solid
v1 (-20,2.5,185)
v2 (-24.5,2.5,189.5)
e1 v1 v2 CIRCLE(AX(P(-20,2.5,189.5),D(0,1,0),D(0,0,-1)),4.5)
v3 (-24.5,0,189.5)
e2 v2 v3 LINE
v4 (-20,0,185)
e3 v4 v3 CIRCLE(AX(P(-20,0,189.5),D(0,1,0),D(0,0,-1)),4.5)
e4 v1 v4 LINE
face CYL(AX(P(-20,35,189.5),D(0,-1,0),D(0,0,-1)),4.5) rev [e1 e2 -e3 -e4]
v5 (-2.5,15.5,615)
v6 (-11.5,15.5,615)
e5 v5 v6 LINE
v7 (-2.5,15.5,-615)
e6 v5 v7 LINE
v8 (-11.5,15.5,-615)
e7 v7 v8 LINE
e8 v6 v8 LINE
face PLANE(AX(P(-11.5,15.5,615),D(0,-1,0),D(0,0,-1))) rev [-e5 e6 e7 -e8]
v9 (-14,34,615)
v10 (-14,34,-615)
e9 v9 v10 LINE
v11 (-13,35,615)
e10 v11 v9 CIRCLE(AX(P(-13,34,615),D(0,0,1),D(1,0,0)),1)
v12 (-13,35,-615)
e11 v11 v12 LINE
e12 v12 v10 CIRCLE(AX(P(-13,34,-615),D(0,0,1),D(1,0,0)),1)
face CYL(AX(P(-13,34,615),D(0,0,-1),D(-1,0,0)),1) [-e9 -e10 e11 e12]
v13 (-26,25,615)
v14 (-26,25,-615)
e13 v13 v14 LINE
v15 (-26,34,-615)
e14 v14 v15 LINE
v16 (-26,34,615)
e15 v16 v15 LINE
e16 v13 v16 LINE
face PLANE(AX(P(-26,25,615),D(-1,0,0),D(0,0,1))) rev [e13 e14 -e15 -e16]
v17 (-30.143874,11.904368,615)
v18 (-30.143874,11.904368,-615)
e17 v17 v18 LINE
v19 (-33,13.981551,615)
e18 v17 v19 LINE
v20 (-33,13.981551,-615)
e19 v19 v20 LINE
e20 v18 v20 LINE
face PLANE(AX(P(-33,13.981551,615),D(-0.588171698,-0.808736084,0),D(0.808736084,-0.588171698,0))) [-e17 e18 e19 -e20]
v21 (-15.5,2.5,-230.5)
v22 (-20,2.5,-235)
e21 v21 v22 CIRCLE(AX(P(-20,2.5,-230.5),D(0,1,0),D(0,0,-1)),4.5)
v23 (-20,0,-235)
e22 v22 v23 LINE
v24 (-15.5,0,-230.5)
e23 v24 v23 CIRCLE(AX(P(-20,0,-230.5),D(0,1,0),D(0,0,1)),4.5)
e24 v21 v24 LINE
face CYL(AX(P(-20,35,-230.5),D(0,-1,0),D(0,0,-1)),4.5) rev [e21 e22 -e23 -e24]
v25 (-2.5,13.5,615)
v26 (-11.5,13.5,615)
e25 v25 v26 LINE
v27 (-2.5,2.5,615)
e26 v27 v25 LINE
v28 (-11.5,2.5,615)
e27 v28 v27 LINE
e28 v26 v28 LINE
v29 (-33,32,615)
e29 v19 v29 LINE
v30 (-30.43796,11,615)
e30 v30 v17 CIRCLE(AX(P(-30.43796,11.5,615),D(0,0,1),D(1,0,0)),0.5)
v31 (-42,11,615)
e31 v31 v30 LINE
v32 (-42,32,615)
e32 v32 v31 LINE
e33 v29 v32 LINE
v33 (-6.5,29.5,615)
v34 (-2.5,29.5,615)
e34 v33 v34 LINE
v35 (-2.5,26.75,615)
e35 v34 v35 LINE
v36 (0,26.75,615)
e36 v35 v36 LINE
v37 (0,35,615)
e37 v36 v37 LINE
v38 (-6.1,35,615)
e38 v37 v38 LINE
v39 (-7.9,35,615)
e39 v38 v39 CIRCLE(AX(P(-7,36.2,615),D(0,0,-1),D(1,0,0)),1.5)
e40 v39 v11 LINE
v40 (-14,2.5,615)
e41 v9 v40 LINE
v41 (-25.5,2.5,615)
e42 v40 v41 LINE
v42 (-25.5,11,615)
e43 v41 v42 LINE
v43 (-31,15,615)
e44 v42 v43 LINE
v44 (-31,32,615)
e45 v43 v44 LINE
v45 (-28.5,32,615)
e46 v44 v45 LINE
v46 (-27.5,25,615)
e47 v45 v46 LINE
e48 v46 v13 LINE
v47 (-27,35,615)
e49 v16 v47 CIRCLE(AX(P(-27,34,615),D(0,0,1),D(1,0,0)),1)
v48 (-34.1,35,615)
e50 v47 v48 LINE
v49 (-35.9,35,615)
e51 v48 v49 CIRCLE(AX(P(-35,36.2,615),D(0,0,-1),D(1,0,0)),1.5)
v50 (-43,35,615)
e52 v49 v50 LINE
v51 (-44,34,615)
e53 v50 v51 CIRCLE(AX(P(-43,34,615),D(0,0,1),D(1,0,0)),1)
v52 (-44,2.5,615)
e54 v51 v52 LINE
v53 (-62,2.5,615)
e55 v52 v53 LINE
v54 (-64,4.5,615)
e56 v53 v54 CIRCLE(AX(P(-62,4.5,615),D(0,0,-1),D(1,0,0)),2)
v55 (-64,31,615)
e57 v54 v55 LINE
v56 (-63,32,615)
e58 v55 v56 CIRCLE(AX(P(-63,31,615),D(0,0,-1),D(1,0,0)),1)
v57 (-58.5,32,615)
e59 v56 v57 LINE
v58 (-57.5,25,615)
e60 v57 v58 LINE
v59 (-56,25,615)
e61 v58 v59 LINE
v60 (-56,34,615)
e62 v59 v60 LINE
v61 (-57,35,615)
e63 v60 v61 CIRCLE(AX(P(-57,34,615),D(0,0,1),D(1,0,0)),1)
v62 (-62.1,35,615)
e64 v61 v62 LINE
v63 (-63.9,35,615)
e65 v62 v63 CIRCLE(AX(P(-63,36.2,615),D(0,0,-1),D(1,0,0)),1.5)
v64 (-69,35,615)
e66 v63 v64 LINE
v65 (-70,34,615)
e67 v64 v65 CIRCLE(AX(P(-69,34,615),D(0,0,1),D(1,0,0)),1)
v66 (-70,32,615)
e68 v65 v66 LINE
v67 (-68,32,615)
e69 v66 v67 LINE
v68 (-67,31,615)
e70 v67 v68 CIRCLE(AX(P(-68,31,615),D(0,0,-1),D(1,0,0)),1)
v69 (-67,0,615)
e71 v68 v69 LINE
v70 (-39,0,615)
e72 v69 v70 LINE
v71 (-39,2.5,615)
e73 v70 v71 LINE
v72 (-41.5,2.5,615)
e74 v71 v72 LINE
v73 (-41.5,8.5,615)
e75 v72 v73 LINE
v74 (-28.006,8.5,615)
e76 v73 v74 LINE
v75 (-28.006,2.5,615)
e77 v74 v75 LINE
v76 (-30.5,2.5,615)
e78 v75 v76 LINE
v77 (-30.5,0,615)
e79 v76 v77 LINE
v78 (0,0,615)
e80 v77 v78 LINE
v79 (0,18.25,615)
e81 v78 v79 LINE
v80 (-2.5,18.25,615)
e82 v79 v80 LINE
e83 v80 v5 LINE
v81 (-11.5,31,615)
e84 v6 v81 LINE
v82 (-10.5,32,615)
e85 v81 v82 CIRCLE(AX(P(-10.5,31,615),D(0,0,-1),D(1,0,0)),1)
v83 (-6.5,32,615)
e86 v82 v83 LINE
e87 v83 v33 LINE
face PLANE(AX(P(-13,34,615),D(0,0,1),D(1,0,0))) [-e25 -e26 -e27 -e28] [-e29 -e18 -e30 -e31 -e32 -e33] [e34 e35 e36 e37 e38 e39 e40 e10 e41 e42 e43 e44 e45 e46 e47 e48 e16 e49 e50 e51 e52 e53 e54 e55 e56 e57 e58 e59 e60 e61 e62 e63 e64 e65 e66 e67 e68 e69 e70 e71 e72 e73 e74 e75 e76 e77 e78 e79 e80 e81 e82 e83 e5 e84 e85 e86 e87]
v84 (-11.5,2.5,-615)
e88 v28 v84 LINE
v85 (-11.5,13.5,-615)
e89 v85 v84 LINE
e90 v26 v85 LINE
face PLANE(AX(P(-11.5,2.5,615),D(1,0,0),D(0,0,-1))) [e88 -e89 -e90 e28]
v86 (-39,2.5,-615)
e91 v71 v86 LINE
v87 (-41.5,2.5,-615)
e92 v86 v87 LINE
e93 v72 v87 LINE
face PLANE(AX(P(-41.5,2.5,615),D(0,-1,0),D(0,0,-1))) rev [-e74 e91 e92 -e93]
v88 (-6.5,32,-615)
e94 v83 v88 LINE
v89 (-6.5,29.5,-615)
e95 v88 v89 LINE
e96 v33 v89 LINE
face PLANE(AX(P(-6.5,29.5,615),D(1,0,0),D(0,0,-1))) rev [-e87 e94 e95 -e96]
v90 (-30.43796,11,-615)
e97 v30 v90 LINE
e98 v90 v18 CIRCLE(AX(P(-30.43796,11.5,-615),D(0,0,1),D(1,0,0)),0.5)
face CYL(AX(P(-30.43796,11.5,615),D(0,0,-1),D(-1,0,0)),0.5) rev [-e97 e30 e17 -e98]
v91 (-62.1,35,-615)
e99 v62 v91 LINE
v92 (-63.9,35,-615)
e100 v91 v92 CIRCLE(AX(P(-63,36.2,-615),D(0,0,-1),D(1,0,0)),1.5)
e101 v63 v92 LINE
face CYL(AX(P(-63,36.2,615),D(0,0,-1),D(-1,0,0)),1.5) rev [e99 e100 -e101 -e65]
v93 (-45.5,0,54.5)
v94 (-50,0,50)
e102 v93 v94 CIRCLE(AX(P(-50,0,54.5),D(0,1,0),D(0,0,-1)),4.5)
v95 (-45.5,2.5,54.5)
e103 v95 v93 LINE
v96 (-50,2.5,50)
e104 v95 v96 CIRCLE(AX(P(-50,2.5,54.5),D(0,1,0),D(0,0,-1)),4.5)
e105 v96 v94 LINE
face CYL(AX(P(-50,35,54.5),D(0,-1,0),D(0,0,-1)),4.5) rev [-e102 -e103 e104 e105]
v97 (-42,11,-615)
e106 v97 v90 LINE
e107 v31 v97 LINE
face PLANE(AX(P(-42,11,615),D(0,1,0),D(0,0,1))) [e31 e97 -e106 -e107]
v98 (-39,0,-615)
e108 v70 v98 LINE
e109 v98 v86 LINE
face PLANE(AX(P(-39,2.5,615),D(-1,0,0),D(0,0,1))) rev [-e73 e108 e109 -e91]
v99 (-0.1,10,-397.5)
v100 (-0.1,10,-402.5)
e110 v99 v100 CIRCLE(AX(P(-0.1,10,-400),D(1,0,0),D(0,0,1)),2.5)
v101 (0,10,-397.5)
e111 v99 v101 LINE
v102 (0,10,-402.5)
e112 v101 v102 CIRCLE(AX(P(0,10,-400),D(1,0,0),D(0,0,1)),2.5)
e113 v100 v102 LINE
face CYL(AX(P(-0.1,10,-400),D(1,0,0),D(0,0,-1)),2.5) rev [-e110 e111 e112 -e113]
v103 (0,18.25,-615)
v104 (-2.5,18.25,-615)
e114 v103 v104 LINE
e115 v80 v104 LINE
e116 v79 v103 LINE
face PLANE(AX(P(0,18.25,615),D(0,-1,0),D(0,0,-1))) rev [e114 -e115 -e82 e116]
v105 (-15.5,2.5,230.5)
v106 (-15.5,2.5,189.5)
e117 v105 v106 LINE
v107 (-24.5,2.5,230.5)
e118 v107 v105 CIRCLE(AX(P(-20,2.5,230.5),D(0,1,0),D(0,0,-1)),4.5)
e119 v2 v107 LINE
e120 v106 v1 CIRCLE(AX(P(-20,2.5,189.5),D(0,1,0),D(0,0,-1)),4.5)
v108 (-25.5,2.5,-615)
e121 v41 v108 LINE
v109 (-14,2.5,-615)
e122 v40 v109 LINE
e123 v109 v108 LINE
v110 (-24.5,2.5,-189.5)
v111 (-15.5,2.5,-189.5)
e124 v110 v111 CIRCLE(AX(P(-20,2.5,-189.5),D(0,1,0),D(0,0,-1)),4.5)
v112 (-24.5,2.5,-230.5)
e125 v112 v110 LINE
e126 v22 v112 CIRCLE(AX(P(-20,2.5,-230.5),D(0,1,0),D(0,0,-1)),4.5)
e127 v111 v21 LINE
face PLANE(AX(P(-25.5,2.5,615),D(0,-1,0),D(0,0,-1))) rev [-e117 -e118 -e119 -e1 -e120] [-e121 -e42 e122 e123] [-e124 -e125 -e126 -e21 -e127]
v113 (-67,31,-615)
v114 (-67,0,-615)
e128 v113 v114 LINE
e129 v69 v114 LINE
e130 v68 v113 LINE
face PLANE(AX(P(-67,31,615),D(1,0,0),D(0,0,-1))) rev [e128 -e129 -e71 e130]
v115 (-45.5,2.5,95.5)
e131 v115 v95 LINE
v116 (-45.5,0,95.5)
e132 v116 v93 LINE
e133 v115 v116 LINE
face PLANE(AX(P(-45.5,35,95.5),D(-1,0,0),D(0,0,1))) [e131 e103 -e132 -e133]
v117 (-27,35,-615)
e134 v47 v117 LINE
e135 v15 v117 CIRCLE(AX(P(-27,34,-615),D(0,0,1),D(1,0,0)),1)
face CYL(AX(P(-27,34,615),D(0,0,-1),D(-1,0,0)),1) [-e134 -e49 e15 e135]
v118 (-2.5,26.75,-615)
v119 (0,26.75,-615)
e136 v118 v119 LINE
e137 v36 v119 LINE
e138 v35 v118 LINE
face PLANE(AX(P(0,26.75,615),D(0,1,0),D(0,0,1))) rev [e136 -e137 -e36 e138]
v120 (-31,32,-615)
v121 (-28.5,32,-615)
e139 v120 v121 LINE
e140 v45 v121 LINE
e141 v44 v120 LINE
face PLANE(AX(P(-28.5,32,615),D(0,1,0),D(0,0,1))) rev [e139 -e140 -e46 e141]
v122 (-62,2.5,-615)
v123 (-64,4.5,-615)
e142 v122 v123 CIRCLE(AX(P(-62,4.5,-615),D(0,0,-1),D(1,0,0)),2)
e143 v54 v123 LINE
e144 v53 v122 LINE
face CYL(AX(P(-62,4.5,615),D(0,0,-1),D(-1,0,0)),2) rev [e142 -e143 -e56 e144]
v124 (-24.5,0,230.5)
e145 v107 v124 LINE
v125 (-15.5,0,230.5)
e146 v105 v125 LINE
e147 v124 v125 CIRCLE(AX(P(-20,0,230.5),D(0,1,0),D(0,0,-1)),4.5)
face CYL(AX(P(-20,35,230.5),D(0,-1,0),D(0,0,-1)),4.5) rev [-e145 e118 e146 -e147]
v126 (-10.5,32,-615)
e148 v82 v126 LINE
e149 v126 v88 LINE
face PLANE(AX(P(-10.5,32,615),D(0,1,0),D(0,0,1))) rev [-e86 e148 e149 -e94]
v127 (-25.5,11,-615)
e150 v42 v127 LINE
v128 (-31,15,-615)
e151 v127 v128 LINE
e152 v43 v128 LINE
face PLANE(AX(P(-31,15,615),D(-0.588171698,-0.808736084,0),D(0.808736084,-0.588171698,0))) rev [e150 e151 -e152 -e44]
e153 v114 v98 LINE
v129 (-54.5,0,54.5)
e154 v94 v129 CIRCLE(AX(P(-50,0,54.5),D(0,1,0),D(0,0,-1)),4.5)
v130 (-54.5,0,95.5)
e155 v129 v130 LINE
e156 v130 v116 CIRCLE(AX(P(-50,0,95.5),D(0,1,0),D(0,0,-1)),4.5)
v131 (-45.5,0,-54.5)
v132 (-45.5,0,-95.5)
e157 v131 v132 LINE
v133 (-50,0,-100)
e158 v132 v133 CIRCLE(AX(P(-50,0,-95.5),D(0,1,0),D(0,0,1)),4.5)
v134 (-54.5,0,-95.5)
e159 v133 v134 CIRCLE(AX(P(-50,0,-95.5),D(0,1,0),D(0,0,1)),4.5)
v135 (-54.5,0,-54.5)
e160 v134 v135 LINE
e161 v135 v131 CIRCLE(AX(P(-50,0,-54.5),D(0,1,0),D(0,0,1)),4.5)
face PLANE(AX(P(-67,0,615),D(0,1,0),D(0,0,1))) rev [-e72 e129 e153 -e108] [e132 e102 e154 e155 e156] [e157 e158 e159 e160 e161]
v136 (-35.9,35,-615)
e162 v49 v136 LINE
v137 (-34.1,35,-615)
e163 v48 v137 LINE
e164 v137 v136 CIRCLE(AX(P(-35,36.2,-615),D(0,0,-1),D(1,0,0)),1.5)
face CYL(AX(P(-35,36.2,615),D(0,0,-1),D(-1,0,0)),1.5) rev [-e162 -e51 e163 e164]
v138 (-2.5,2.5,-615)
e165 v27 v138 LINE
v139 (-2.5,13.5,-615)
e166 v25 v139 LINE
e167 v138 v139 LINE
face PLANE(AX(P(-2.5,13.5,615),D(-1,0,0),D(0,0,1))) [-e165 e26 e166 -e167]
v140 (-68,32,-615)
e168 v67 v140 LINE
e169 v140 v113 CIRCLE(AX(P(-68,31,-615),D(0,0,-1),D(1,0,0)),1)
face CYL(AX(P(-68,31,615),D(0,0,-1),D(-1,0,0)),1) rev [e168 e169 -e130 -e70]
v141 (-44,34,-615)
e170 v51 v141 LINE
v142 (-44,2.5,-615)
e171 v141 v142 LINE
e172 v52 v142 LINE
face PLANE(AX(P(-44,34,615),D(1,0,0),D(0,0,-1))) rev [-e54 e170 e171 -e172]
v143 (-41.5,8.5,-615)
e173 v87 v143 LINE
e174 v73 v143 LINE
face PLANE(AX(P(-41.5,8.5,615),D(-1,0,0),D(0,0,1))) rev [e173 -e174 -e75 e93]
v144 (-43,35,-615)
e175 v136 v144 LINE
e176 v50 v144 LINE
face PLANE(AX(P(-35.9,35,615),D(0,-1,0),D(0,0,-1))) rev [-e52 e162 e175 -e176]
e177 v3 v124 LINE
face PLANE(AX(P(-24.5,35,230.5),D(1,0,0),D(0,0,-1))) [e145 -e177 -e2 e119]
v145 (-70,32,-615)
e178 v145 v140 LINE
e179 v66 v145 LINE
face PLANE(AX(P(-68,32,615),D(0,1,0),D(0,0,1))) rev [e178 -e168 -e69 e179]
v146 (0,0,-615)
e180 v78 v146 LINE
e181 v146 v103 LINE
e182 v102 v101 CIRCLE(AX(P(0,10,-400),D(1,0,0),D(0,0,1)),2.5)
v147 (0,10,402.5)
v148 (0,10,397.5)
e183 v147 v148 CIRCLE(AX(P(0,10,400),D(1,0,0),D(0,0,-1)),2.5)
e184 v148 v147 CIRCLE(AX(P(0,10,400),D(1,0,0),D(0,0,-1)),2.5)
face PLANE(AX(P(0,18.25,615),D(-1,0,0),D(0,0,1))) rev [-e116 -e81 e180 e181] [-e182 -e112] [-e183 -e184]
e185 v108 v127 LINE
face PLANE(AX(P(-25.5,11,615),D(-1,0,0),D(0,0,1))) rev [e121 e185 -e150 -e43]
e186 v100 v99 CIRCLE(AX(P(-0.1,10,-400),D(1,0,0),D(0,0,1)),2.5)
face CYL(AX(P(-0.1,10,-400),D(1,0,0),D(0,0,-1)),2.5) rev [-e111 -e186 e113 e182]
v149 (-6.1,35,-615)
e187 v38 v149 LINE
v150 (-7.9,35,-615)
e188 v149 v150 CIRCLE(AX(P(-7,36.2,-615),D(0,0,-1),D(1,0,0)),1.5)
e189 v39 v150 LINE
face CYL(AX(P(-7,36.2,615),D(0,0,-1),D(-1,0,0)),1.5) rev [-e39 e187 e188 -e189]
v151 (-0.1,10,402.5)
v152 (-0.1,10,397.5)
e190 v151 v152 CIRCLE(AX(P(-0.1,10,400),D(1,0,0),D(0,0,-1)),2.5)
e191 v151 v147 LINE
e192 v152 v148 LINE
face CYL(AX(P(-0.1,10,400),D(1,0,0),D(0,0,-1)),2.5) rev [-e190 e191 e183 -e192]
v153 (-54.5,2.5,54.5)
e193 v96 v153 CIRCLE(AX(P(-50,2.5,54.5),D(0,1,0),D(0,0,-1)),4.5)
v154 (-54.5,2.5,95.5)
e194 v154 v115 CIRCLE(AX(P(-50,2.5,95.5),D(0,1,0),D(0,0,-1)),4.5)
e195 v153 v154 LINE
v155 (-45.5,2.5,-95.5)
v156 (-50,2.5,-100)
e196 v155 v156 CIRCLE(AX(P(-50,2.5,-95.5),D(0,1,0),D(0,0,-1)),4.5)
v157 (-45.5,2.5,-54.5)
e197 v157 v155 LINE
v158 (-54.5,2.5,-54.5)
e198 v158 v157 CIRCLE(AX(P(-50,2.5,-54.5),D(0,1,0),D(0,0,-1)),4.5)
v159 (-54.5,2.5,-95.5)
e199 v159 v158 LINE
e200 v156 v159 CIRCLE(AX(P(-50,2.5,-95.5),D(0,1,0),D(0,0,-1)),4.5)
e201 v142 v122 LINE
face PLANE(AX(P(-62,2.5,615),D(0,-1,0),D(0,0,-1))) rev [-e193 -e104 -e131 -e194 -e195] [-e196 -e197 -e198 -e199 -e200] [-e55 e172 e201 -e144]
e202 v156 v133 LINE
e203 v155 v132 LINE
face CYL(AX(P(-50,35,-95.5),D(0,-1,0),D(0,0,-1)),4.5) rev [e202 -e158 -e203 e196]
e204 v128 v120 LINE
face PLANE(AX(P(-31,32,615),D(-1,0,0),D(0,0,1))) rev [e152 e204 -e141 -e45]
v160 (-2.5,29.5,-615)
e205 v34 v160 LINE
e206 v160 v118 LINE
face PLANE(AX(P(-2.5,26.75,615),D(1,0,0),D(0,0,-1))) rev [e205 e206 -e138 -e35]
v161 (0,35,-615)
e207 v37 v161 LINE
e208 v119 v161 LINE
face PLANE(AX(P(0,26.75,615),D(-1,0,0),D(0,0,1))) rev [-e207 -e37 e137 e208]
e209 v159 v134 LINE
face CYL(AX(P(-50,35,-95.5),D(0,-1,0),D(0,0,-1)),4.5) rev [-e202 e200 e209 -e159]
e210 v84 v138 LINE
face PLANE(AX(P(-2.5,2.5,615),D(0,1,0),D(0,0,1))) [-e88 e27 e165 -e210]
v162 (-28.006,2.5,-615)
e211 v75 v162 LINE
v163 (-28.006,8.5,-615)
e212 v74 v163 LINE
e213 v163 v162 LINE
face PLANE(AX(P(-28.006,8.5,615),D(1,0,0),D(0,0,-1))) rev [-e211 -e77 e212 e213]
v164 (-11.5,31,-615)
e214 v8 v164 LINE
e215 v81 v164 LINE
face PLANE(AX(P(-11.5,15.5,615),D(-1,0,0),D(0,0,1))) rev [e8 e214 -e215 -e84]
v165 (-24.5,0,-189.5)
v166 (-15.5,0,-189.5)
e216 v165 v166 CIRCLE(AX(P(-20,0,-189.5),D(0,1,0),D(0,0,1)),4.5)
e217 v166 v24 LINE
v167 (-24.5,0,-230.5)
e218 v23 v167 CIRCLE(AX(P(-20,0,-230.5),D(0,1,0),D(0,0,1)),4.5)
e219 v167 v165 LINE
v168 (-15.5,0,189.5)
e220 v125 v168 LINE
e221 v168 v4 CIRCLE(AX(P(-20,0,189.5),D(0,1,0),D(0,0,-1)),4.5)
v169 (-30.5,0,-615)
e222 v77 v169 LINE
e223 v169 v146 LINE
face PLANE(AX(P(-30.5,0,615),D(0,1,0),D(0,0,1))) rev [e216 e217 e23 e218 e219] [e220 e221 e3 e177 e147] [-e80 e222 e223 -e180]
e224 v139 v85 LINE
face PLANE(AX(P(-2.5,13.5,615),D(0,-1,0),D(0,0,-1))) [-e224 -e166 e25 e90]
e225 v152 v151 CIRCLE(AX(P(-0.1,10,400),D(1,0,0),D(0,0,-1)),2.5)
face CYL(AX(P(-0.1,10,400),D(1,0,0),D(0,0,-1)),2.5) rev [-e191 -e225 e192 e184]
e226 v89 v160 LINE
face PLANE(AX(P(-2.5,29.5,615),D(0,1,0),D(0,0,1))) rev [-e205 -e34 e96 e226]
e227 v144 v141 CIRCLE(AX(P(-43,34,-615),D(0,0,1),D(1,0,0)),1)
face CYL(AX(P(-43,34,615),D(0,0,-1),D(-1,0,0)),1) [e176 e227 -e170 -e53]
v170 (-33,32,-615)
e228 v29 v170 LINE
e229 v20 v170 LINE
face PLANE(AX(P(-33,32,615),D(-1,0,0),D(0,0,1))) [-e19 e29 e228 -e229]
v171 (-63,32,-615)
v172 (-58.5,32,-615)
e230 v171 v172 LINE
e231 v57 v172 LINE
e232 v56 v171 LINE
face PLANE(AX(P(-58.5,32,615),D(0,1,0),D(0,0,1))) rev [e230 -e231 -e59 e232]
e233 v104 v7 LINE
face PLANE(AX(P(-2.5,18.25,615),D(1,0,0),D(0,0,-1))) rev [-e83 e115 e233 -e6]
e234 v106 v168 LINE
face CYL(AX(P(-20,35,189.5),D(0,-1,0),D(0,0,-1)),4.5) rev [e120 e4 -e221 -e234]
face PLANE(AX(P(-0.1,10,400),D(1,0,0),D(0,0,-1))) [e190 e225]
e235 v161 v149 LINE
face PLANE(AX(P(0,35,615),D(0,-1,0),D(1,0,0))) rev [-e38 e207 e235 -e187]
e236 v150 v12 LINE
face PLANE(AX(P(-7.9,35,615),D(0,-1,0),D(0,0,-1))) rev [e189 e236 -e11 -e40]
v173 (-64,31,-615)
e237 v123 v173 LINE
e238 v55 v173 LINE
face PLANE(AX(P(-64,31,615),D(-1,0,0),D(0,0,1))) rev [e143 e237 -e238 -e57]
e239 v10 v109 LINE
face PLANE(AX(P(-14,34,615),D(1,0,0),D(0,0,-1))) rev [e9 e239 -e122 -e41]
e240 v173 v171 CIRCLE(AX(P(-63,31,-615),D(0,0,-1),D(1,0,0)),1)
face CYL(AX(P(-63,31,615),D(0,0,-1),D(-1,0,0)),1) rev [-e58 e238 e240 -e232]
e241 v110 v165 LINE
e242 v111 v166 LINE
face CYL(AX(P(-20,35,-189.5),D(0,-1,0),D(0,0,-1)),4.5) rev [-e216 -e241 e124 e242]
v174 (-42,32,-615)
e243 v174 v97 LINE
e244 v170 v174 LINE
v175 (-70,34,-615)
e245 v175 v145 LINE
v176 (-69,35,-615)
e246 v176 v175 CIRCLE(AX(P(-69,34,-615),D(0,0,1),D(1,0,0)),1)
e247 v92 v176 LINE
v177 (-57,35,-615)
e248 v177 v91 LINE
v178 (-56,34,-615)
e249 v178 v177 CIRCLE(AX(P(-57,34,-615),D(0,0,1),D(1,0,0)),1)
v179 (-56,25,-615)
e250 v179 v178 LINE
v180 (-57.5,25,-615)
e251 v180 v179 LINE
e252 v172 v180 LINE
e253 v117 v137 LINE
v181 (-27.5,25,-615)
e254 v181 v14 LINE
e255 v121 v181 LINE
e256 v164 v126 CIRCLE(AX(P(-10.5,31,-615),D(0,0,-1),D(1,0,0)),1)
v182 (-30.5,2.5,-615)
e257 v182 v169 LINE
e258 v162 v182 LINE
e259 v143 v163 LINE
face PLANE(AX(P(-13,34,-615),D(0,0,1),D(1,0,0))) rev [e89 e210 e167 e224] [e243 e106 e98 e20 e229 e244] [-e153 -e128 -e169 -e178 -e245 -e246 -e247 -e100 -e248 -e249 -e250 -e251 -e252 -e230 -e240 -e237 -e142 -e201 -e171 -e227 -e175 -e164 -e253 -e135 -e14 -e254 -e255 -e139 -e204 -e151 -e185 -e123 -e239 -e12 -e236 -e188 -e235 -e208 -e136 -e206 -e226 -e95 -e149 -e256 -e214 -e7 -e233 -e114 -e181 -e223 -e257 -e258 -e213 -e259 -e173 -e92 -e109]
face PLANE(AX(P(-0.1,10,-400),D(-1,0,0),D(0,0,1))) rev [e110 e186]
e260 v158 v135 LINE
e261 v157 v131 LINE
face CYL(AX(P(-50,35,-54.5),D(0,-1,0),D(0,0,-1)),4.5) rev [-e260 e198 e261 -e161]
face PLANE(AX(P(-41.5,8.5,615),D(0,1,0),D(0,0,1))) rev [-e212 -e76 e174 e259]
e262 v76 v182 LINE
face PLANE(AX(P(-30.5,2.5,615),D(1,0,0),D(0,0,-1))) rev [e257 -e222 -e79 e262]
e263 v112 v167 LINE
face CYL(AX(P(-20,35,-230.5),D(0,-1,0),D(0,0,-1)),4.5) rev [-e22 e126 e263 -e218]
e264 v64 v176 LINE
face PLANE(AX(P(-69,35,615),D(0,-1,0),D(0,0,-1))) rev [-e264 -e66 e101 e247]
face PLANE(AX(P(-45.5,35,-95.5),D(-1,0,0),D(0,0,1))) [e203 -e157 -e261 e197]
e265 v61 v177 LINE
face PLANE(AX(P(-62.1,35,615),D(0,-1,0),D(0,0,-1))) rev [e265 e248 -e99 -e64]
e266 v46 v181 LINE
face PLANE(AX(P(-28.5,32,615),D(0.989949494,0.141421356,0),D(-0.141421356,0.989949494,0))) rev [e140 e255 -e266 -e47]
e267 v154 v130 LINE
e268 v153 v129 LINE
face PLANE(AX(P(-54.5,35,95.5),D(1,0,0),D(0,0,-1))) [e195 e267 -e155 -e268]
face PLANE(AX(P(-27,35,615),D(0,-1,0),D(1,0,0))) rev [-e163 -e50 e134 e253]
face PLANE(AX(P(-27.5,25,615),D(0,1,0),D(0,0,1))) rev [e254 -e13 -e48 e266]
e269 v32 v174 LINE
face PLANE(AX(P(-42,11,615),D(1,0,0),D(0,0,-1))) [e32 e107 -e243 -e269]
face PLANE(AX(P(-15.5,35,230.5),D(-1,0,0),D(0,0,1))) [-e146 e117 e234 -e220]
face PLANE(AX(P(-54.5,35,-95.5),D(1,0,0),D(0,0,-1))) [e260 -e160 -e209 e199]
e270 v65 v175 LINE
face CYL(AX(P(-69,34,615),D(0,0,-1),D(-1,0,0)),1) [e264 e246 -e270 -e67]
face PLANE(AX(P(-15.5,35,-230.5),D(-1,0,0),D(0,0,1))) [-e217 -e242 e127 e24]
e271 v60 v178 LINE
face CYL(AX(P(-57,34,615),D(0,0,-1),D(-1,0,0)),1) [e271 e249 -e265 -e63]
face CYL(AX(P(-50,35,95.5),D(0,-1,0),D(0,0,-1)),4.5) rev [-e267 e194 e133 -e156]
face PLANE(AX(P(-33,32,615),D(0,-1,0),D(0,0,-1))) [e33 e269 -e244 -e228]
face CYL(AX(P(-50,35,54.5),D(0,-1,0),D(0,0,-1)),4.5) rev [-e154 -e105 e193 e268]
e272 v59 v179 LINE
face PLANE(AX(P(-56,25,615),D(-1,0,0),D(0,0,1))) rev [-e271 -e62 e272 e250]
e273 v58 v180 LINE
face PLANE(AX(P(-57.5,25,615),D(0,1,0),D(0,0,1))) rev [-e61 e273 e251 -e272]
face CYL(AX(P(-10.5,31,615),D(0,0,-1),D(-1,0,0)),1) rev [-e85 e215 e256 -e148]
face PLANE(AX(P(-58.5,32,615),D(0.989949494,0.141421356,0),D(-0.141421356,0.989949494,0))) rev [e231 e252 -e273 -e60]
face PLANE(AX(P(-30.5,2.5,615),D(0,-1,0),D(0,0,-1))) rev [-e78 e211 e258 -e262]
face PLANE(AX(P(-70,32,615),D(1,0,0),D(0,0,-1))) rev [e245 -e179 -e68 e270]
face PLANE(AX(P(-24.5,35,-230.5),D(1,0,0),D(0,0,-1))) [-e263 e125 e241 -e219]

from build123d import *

# Parameters (mm, degrees)
SKETCH_1_W               = 9
SKETCH_1_H               = 11
EXTRUDE_1_DEPTH          = 615
CUT_EXTRUDE_1_DEPTH      = 620.823563605
CUT_EXTRUDE_1_DEPTH_BACK = 620.823563605
SKETCH_3_R               = 2.5
CUT_EXTRUDE_2_DEPTH      = 0.1


with BuildPart() as part:
    # 草图1 → 凸台-拉伸1 (new, symmetric)
    with BuildSketch(Plane.XY):
        with BuildLine():
            Line((-28.5, 32), (-27.5, 25))
            Line((-27.5, 25), (-26, 25))
            Line((-26, 25), (-26, 34))
            ThreePointArc((-26, 34), (-26.292893219, 34.707106781), (-27, 35))
            Line((-27, 35), (-34.1, 35))
            ThreePointArc((-34.1, 35), (-35, 34.7), (-35.9, 35))
            Line((-35.9, 35), (-43, 35))
            ThreePointArc((-43, 35), (-43.707106781, 34.707106781), (-44, 34))
            Line((-44, 34), (-44, 2.5))
            Line((-44, 2.5), (-62, 2.5))
            ThreePointArc((-62, 2.5), (-63.414213562, 3.085786438), (-64, 4.5))
            Line((-64, 4.5), (-64, 31))
            ThreePointArc((-64, 31), (-63.707106781, 31.707106781), (-63, 32))
            Line((-63, 32), (-58.5, 32))
            Line((-58.5, 32), (-57.5, 25))
            Line((-57.5, 25), (-56, 25))
            Line((-56, 25), (-56, 34))
            ThreePointArc((-56, 34), (-56.292893219, 34.707106781), (-57, 35))
            Line((-57, 35), (-62.1, 35))
            ThreePointArc((-62.1, 35), (-63, 34.7), (-63.9, 35))
            Line((-63.9, 35), (-69, 35))
            ThreePointArc((-69, 35), (-69.707106781, 34.707106781), (-70, 34))
            Line((-70, 34), (-70, 32))
            Line((-70, 32), (-68, 32))
            ThreePointArc((-68, 32), (-67.292893219, 31.707106781), (-67, 31))
            Line((-67, 31), (-67, 0))
            Line((-67, 0), (-39, 0))
            Line((-39, 0), (-39, 2.5))
            Line((-39, 2.5), (-41.5, 2.5))
            Line((-41.5, 2.5), (-41.5, 8.5))
            Line((-41.5, 8.5), (-28.006, 8.5))
            Line((-28.006, 8.5), (-28.006, 2.5))
            Line((-28.006, 2.5), (-30.5, 2.5))
            Line((-30.5, 2.5), (-30.5, 0))
            Line((-30.5, 0), (0, 0))
            Line((0, 0), (0, 18.25))
            Line((0, 18.25), (-2.5, 18.25))
            Line((-2.5, 18.25), (-2.5, 15.5))
            Line((-2.5, 15.5), (-11.5, 15.5))
            Line((-11.5, 15.5), (-11.5, 31))
            ThreePointArc((-11.5, 31), (-11.207106781, 31.707106781), (-10.5, 32))
            Line((-10.5, 32), (-6.5, 32))
            Line((-6.5, 32), (-6.5, 29.5))
            Line((-6.5, 29.5), (-2.5, 29.5))
            Line((-2.5, 29.5), (-2.5, 26.75))
            Line((-2.5, 26.75), (0, 26.75))
            Line((0, 26.75), (0, 35))
            Line((0, 35), (-6.1, 35))
            ThreePointArc((-6.1, 35), (-7, 34.7), (-7.9, 35))
            Line((-7.9, 35), (-13, 35))
            ThreePointArc((-13, 35), (-13.707106781, 34.707106781), (-14, 34))
            Line((-14, 34), (-14, 2.5))
            Line((-14, 2.5), (-25.5, 2.5))
            Line((-25.5, 2.5), (-25.5, 11))
            Line((-25.5, 11), (-31, 15))
            Line((-31, 15), (-31, 32))
            Line((-31, 32), (-28.5, 32))
        make_face()
        with Locations((-7, 8)):
            Rectangle(SKETCH_1_W, SKETCH_1_H, mode=Mode.SUBTRACT)
        with BuildLine():
            Line((-42, 11), (-42, 32))
            Line((-42, 32), (-33, 32))
            Line((-33, 32), (-33, 13.981550817))
            Line((-33, 13.981550817), (-30.143873685, 11.904368042))
            ThreePointArc((-30.143873685, 11.904368042), (-29.962468198, 11.345377914), (-30.437959534, 11))
            Line((-30.437959534, 11), (-42, 11))
        make_face(mode=Mode.SUBTRACT)
    extrude(amount=EXTRUDE_1_DEPTH, both=True)

    # 草图2 → 切除-拉伸1 (cut, two sides: drawn at the far end of the back side and taken through both)
    with BuildSketch(Plane(origin=(0, 2.5, 0), x_dir=(1, 0, 0), z_dir=(0, 1, 0)).offset(-CUT_EXTRUDE_1_DEPTH_BACK)):
        with BuildLine():
            Line((-15.5, -230.5), (-15.5, -189.5))
            ThreePointArc((-15.5, -189.5), (-20, -185), (-24.5, -189.5))
            Line((-24.5, -189.5), (-24.5, -230.5))
            ThreePointArc((-24.5, -230.5), (-20, -235), (-15.5, -230.5))
        make_face()
        with BuildLine():
            Line((-45.5, 95.5), (-45.5, 54.5))
            ThreePointArc((-45.5, 54.5), (-50, 50), (-54.5, 54.5))
            Line((-54.5, 54.5), (-54.5, 95.5))
            ThreePointArc((-54.5, 95.5), (-50, 100), (-45.5, 95.5))
        make_face()
        with BuildLine():
            Line((-45.5, -95.5), (-45.5, -54.5))
            ThreePointArc((-45.5, -54.5), (-50, -50), (-54.5, -54.5))
            Line((-54.5, -54.5), (-54.5, -95.5))
            ThreePointArc((-54.5, -95.5), (-50, -100), (-45.5, -95.5))
        make_face()
        with BuildLine():
            Line((-15.5, 230.5), (-15.5, 189.5))
            ThreePointArc((-15.5, 189.5), (-20, 185), (-24.5, 189.5))
            Line((-24.5, 189.5), (-24.5, 230.5))
            ThreePointArc((-24.5, 230.5), (-20, 235), (-15.5, 230.5))
        make_face()
    extrude(amount=CUT_EXTRUDE_1_DEPTH + CUT_EXTRUDE_1_DEPTH_BACK, mode=Mode.SUBTRACT)

    # 草图3 → 切除-拉伸2 (cut)
    with BuildSketch(Plane(origin=(0, 0, 0), x_dir=(0, 0, -1), z_dir=(1, 0, 0))):
        with Locations((-400, 10)):
            Circle(SKETCH_3_R)
        with Locations(Location((400, 10, 0), (0, 0, 180))):
            Circle(SKETCH_3_R)
    extrude(amount=-CUT_EXTRUDE_2_DEPTH, mode=Mode.SUBTRACT)


solid = part.part
